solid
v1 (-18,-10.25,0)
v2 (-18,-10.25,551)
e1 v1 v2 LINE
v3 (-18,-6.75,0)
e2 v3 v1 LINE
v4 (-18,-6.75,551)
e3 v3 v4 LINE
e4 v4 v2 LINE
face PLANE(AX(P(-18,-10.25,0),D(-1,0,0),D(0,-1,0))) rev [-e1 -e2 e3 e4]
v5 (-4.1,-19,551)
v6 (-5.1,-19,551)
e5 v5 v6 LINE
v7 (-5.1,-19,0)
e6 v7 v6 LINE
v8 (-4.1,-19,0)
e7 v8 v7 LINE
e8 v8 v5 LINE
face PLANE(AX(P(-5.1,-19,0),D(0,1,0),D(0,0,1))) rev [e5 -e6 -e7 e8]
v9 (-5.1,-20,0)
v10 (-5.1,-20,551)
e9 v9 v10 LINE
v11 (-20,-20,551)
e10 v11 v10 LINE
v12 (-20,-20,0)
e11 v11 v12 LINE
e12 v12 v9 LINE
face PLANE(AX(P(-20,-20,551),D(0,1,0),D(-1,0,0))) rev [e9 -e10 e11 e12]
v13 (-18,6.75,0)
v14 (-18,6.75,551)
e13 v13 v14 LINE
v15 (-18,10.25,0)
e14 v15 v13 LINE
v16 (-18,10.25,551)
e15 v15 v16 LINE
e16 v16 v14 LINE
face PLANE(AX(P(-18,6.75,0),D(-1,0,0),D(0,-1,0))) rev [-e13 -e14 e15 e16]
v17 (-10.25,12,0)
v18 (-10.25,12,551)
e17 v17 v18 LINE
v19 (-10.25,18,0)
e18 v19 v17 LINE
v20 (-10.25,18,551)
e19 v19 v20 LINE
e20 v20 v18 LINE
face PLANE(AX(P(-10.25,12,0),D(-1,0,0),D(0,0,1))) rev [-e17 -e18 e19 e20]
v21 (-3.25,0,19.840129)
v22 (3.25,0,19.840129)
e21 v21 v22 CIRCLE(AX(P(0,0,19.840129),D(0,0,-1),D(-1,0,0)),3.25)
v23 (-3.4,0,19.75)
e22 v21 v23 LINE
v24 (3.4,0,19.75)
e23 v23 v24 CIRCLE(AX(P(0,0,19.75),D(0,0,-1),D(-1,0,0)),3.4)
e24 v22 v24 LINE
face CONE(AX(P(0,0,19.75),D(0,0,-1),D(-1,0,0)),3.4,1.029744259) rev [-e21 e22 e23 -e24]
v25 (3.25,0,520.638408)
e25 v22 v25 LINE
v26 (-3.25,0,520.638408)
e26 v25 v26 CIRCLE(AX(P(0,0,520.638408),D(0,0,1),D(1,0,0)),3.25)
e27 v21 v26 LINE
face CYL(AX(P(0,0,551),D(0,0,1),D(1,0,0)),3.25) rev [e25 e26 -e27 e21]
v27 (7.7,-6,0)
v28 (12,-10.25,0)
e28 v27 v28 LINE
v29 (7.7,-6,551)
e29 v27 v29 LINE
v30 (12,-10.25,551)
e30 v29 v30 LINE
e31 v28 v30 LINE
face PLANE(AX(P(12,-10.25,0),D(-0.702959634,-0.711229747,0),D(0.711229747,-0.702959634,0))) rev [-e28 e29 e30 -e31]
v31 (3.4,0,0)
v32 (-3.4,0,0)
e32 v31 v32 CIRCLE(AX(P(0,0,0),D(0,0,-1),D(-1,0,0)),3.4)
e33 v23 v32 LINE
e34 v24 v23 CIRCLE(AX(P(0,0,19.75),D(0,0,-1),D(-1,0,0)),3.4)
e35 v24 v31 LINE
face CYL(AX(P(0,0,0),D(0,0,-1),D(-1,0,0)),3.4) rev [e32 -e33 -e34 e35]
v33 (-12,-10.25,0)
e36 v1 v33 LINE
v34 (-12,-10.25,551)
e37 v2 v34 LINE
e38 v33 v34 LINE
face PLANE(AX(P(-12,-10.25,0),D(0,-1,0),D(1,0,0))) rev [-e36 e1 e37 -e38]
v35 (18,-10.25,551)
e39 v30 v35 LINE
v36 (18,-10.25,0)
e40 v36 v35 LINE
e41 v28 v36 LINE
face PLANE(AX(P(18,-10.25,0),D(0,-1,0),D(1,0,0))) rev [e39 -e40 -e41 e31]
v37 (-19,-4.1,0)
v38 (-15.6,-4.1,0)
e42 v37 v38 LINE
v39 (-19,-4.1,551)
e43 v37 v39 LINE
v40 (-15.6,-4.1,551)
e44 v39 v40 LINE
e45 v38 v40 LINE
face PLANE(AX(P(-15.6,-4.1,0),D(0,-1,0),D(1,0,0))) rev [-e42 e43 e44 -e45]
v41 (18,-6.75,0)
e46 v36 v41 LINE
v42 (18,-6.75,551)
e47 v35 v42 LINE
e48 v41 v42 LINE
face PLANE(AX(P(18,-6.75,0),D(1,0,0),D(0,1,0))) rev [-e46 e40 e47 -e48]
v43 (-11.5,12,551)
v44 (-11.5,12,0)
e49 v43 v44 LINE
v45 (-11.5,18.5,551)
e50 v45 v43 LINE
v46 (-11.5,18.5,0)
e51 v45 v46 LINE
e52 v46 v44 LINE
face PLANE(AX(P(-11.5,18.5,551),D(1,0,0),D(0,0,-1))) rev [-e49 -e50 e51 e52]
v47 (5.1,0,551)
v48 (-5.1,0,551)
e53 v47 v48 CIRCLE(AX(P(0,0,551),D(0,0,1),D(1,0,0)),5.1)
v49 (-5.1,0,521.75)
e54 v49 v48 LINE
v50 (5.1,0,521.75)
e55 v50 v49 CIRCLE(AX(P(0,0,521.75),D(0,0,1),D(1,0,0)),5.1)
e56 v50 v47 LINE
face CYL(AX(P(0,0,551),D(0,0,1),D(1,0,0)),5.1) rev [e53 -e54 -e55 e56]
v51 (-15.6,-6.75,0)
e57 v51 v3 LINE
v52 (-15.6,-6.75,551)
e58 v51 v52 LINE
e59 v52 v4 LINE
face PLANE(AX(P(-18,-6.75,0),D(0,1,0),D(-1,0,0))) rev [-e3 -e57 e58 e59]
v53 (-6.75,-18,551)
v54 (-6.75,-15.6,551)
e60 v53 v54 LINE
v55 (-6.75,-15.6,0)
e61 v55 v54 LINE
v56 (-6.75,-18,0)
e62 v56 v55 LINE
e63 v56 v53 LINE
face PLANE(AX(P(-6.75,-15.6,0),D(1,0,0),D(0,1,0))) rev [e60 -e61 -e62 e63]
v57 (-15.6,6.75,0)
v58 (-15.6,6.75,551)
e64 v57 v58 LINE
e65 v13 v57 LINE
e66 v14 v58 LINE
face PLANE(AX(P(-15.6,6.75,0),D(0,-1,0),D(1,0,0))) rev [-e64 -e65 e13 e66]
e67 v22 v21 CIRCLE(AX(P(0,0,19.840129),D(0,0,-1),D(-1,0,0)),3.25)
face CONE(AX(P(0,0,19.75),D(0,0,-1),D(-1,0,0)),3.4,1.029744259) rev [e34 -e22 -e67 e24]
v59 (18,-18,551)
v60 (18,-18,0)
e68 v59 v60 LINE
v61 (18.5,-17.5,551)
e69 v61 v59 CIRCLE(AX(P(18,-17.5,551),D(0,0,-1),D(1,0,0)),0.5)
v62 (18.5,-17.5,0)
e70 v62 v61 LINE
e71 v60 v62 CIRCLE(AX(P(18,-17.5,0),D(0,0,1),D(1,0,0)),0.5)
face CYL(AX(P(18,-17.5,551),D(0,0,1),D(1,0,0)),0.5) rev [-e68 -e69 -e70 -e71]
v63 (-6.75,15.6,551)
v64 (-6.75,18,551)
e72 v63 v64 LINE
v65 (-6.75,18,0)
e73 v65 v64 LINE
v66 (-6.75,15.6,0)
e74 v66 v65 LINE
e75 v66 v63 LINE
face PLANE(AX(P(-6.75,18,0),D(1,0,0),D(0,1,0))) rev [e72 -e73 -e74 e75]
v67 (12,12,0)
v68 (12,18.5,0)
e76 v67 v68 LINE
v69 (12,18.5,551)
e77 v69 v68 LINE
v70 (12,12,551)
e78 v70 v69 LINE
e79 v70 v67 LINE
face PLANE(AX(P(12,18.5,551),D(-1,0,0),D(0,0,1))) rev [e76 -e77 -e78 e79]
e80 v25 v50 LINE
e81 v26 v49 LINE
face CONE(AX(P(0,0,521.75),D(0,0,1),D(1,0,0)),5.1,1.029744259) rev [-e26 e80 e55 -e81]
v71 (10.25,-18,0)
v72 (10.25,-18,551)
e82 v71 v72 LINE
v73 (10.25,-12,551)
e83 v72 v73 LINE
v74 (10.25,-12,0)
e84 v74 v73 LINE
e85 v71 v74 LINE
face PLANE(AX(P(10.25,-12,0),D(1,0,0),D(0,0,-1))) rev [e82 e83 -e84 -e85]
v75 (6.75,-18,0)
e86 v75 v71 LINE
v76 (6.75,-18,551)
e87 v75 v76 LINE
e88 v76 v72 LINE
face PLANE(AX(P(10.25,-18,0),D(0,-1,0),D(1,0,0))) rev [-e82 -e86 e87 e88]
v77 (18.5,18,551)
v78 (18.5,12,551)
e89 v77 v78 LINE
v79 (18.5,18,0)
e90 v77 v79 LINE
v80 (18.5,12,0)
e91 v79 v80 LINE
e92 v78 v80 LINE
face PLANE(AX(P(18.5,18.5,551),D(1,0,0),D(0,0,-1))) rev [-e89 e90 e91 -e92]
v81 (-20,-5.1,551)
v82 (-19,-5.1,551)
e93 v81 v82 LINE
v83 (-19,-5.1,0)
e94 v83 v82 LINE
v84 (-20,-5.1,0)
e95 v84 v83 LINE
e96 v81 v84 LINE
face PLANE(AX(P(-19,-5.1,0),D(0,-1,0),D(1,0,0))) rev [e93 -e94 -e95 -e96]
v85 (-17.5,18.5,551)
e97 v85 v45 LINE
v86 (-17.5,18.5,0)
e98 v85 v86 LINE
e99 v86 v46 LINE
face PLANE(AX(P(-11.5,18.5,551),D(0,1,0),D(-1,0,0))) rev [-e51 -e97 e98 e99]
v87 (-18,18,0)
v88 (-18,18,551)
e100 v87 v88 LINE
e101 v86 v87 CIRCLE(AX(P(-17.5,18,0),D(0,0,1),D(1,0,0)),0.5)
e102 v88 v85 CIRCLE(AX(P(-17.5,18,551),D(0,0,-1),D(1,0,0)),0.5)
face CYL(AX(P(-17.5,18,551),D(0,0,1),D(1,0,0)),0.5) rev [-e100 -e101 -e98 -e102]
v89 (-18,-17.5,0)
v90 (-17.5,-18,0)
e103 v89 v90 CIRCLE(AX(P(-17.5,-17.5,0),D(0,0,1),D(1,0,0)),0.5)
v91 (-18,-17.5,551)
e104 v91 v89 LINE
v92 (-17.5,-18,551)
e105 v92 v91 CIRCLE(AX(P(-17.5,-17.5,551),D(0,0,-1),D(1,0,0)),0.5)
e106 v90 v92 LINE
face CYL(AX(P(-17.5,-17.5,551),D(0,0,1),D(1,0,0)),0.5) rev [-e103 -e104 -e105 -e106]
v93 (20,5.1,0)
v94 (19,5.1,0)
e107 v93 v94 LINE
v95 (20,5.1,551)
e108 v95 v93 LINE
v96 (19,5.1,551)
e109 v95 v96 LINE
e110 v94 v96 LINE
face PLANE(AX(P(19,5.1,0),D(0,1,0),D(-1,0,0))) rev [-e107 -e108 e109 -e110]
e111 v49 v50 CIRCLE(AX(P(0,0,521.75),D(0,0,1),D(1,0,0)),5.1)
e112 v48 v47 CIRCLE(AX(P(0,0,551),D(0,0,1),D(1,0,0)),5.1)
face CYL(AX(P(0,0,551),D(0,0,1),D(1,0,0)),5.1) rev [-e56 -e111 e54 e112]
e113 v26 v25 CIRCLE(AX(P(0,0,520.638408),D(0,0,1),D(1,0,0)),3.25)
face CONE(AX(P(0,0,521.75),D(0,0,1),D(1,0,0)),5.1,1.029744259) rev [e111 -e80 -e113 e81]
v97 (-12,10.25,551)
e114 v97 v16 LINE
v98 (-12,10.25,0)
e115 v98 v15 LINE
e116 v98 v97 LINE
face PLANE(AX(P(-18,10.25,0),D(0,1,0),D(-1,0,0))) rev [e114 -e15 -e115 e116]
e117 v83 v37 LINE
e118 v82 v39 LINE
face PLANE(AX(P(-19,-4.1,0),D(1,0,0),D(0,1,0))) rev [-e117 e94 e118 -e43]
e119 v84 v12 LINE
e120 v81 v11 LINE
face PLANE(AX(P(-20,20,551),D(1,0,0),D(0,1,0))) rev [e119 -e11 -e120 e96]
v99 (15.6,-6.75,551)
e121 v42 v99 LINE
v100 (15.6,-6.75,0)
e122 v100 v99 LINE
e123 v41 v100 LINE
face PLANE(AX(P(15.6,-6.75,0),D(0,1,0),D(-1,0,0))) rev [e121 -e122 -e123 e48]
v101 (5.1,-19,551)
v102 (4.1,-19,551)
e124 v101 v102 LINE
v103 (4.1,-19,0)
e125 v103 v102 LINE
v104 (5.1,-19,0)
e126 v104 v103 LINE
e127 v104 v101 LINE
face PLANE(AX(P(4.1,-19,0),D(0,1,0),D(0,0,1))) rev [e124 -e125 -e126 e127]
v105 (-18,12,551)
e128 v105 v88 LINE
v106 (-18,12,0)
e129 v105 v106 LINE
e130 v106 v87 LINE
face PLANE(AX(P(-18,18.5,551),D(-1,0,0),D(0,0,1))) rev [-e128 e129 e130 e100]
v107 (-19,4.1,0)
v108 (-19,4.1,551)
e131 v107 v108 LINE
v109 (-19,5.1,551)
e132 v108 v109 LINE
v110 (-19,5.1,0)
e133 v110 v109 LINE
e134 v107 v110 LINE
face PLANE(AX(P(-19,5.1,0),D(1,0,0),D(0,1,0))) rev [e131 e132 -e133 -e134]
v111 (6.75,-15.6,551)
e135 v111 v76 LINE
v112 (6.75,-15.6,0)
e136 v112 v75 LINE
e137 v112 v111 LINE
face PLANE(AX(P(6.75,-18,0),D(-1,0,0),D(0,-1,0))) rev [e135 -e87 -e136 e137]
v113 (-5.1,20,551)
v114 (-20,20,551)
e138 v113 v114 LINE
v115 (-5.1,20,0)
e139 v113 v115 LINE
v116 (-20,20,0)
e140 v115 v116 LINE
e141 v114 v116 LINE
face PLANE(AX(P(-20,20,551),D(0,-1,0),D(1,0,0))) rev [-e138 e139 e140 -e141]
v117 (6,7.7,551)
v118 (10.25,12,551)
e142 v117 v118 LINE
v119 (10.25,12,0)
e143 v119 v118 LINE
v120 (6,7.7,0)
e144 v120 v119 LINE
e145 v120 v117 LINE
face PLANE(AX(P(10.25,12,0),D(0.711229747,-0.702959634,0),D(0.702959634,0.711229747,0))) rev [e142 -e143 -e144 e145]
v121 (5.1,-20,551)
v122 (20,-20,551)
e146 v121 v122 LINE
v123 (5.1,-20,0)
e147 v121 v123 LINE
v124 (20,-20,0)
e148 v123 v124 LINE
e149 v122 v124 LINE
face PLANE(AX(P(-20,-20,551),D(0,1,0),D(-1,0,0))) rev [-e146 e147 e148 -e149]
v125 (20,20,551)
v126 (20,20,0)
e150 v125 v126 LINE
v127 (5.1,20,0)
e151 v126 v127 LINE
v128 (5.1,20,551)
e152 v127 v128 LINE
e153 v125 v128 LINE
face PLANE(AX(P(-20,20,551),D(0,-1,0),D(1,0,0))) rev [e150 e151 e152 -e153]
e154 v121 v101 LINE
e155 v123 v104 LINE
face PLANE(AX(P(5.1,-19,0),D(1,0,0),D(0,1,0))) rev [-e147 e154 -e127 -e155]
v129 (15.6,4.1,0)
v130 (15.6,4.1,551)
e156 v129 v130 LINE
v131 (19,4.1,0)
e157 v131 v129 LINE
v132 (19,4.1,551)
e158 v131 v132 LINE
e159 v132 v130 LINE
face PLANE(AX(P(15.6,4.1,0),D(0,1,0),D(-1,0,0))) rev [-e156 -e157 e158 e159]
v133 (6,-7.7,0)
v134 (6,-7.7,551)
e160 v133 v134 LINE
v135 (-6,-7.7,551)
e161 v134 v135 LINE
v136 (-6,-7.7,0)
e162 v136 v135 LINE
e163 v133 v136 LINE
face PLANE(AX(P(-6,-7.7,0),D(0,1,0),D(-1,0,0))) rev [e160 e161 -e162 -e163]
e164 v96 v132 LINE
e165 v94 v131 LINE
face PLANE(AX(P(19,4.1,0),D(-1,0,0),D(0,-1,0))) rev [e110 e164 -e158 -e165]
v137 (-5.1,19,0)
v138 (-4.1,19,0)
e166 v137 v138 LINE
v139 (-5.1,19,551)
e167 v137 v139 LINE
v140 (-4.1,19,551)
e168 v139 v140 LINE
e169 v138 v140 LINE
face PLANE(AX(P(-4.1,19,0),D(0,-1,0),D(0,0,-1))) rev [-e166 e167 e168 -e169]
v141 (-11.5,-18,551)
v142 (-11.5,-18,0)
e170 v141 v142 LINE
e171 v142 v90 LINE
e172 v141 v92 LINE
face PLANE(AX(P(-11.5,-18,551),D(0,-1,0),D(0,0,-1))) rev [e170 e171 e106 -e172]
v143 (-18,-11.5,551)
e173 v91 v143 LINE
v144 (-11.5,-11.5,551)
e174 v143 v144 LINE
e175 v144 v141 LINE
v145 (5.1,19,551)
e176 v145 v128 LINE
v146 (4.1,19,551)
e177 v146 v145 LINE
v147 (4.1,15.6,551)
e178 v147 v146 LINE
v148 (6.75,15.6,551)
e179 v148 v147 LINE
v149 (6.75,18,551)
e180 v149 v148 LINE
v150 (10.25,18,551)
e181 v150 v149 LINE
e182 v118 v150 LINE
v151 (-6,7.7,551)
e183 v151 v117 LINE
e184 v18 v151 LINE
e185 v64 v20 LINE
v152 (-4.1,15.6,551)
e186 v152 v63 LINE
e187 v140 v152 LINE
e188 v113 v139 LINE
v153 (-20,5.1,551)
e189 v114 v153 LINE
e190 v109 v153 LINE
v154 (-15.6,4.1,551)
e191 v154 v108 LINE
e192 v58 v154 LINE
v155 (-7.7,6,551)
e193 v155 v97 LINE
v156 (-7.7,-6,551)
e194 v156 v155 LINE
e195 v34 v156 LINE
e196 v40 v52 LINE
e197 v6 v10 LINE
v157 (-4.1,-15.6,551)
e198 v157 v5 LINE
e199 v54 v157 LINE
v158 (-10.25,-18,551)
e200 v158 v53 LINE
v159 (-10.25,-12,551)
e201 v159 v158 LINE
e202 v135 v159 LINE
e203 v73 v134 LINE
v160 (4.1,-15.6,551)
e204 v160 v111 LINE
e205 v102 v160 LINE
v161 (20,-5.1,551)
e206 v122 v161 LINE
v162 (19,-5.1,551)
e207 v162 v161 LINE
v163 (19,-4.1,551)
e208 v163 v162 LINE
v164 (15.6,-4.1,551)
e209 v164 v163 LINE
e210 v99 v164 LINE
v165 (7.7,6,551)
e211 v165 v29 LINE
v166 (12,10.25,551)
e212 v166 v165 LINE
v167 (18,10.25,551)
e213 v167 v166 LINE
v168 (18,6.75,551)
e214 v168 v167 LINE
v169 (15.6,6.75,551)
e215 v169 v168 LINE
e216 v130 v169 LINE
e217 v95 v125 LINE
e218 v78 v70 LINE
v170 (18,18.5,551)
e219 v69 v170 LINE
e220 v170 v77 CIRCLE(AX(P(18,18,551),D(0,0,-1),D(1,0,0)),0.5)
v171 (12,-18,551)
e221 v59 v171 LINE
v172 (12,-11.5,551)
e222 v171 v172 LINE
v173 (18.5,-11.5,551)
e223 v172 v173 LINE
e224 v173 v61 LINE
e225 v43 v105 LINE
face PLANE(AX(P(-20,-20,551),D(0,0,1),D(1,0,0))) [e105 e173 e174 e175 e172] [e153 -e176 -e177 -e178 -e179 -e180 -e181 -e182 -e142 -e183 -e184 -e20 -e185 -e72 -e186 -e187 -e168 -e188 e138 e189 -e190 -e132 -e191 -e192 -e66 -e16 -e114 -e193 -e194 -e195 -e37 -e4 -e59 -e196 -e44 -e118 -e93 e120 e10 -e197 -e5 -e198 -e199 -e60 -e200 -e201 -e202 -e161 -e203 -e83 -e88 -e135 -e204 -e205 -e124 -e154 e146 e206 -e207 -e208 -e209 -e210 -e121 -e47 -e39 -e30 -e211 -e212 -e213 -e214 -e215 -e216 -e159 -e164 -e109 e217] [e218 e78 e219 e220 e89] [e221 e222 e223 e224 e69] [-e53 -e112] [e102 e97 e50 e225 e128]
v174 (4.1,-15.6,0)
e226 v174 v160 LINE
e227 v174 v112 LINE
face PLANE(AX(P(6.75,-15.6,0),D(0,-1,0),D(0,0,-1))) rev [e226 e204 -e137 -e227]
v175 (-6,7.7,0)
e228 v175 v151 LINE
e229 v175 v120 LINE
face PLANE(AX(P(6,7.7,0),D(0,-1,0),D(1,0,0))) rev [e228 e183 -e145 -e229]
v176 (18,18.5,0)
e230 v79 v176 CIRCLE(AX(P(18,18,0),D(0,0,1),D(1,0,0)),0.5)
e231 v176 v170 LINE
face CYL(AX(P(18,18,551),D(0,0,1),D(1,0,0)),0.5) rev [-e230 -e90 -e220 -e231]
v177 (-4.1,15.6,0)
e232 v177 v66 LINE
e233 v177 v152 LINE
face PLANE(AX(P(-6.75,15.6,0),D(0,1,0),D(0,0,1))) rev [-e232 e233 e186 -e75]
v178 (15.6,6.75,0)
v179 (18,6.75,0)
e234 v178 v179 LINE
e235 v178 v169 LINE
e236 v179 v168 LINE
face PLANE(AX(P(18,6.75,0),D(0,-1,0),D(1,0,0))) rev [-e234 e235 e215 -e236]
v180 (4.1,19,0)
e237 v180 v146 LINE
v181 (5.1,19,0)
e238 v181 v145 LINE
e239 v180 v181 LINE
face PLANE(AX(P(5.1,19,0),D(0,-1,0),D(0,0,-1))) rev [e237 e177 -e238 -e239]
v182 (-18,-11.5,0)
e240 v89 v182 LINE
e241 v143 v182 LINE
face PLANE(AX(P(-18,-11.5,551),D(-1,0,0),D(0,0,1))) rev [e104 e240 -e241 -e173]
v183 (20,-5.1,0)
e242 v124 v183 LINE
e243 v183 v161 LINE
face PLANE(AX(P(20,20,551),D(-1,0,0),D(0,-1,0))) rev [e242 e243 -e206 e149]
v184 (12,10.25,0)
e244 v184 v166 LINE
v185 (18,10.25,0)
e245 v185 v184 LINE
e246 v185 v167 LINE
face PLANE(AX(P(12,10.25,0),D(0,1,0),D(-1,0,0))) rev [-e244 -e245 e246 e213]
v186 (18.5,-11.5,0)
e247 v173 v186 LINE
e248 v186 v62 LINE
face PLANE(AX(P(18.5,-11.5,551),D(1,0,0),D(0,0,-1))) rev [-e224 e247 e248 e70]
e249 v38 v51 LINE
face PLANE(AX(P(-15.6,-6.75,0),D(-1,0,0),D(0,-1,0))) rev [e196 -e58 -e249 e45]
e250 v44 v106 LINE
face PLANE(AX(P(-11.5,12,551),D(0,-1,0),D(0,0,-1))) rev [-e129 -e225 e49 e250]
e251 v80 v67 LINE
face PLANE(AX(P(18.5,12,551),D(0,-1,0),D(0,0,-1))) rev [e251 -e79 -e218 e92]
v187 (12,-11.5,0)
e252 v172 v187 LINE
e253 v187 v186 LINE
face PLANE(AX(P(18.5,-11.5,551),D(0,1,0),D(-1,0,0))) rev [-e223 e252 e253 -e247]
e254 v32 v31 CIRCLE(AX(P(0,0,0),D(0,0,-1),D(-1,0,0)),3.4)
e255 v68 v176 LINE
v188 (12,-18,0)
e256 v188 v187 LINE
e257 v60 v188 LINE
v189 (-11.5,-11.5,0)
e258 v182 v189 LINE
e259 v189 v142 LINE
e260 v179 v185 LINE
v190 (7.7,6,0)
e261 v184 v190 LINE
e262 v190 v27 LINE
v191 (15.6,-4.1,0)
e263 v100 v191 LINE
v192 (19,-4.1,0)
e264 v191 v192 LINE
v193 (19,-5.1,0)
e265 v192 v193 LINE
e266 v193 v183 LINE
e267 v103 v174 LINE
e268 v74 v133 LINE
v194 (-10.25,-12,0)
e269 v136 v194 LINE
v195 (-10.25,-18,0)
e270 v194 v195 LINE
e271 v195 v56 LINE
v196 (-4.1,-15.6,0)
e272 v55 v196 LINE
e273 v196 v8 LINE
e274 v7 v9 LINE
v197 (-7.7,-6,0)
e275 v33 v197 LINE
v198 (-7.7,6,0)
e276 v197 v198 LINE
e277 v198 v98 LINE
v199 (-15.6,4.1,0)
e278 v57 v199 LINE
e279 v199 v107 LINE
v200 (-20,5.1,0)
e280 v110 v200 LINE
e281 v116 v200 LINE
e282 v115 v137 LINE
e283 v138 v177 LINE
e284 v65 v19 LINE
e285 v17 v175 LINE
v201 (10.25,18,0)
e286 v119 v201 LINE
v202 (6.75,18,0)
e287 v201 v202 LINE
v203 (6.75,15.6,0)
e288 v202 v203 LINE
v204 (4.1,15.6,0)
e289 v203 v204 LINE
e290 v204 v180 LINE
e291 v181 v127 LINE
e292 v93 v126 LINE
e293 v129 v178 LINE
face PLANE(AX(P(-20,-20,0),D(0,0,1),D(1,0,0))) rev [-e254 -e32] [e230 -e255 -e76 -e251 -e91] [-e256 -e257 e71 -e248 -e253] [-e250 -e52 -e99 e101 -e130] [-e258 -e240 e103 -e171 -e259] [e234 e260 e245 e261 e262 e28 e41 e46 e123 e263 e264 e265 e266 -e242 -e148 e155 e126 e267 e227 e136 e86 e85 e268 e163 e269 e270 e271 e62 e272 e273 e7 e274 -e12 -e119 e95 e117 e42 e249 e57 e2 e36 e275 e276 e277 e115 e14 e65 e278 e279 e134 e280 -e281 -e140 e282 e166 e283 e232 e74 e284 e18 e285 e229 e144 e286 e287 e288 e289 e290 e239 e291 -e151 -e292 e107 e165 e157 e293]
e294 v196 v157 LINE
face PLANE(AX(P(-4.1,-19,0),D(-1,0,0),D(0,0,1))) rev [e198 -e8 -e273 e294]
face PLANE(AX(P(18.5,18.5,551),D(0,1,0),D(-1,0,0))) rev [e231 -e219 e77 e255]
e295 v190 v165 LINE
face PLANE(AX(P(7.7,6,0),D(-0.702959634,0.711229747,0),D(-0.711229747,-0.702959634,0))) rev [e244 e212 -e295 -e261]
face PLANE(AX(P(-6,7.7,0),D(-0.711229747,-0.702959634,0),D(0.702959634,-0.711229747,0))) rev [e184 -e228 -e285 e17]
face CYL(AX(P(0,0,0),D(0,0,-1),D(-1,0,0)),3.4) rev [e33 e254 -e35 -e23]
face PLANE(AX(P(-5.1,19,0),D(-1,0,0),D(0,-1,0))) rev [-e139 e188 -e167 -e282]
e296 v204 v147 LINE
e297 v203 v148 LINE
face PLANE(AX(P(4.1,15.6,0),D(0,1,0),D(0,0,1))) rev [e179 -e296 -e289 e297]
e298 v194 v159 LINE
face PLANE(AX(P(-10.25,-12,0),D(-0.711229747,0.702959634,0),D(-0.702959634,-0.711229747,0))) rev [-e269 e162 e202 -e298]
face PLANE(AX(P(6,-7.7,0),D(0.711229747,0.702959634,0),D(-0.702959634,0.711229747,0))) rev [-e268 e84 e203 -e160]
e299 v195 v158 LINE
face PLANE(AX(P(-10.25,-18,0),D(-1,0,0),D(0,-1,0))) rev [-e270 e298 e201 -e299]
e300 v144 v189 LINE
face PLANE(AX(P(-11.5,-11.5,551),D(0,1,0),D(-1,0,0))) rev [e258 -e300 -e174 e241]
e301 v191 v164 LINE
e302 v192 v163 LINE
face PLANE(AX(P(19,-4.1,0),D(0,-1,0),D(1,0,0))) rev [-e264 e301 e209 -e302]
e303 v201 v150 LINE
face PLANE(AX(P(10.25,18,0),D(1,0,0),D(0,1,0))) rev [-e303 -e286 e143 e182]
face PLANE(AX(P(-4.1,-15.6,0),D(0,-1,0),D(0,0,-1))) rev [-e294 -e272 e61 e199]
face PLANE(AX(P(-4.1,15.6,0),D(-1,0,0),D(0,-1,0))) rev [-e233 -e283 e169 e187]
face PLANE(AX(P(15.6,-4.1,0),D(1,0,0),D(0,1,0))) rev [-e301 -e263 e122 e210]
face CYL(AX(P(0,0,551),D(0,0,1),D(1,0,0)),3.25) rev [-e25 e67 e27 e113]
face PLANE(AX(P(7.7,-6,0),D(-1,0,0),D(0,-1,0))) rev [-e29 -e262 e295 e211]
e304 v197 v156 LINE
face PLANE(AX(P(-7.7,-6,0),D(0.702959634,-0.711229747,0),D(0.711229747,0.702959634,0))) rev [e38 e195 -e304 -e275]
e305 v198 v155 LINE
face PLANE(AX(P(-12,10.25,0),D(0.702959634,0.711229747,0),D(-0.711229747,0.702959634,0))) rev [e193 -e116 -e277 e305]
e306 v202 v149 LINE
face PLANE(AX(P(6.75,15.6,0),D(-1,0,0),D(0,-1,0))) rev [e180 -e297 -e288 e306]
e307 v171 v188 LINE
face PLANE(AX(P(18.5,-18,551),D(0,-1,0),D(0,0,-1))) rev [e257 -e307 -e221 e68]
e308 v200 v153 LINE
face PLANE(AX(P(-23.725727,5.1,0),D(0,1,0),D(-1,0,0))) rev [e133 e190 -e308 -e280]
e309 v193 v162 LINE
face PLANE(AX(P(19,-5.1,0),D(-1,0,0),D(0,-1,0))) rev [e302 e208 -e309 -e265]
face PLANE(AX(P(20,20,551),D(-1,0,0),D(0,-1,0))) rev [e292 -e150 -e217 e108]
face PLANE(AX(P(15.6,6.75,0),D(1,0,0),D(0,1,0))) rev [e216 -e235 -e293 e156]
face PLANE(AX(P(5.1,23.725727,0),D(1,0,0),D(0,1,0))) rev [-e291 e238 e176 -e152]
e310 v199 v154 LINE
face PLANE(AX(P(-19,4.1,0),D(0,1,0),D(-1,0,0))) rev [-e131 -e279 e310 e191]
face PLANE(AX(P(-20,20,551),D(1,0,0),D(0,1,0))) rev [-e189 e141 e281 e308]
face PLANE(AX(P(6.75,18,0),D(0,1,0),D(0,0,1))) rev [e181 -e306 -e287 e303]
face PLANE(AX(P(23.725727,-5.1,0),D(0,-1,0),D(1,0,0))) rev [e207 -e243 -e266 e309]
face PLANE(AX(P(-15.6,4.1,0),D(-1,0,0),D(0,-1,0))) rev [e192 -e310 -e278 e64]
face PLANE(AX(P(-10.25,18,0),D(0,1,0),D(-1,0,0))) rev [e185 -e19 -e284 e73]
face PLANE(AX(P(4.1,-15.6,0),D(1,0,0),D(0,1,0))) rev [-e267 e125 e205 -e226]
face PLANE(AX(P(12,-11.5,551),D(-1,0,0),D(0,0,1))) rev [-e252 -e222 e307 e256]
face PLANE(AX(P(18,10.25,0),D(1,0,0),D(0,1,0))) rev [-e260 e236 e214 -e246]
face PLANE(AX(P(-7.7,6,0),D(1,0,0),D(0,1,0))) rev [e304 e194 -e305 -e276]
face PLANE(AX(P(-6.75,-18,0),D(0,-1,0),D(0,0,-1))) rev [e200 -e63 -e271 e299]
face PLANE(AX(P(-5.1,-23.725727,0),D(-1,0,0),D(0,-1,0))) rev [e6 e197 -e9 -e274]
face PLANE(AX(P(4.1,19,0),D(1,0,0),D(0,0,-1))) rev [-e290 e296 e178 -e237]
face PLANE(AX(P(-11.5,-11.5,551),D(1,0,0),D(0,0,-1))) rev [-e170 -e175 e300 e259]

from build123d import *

# Parameters (mm, degrees)
SKETCH_1_W                  = 40
SKETCH_1_H                  = 40
EXTRUDE_1_DEPTH             = 551
HOLE_WIZARD_6_5_6_5_1_D     = 6.5
CUT_EXTRUDE_1_DEPTH         = 552.725475214
PATTERN_CIRCULAR_1_COUNT    = 4
SKETCH_5_W                  = 6.5
SKETCH_5_H                  = 6.5
CUT_EXTRUDE_2_DEPTH         = 552.725475214
PATTERN_LINEAR_1_COUNT      = 2
PATTERN_LINEAR_1_PITCH      = 30
PATTERN_LINEAR_1_COUNT_DIR2 = 2
PATTERN_LINEAR_1_PITCH_DIR2 = 30
FILLET_2_R                  = 0.5
HOLE_WIZARD_M12_1_D         = 10.2
HOLE_WIZARD_M12_1_DEPTH     = 29.25
HOLE_WIZARD_M12_1_TIP       = 3.064389157
HOLE_WIZARD_M8_2_D          = 6.8
HOLE_WIZARD_M8_2_DEPTH      = 19.75
HOLE_WIZARD_M8_2_TIP        = 2.042926105


with BuildPart() as part:
    # 草图1 → 凸台-拉伸1 (new body)
    with BuildSketch(Plane.XY):
        Rectangle(SKETCH_1_W, SKETCH_1_H)
    extrude(amount=EXTRUDE_1_DEPTH)

    # Ø6.5 (6.5) 直径孔1 (through all)
    with Locations(Plane.XY.offset(551)):
        with Locations((0, 0)):
            Hole(HOLE_WIZARD_6_5_6_5_1_D / 2)

    # 草图4 → 切除-拉伸1 (cut, through all)
    with BuildSketch(Plane.XY.offset(551)):
        Polygon((6, -7.7), (10.25, -12), (10.25, -18), (6.75, -18), (6.75, -15.6), (4.1, -15.6), (4.1, -19), (5.1, -19), (5.1, -23.725727051), (-5.1, -23.725727051), (-5.1, -19), (-4.1, -19), (-4.1, -15.6), (-6.75, -15.6), (-6.75, -18), (-10.25, -18), (-10.25, -12), (-6, -7.7), align=None)
    cut_extrude_1 = extrude(amount=-CUT_EXTRUDE_1_DEPTH, mode=Mode.SUBTRACT)

    # 阵列(圆周)1: 切除-拉伸1 ×4 about axis
    pattern_circular_1_axis = Axis((0, 0, 0), (0, 0, 1))
    for i in range(1, PATTERN_CIRCULAR_1_COUNT):
        add(cut_extrude_1.rotate(pattern_circular_1_axis, i * 360 / PATTERN_CIRCULAR_1_COUNT), mode=Mode.SUBTRACT)

    # 草图5 → 切除-拉伸2 (cut, through all)
    with BuildSketch(Plane(origin=(0, 0, 0), x_dir=(-1, 0, 0), z_dir=(0, 0, -1))):
        with Locations((14.75, -14.75)):
            Rectangle(SKETCH_5_W, SKETCH_5_H)
    cut_extrude_2 = extrude(amount=-CUT_EXTRUDE_2_DEPTH, mode=Mode.SUBTRACT)

    # 阵列(线性)1: Cut-Extrude 2 2 × 2
    with Locations(*[(i * PATTERN_LINEAR_1_PITCH, j * PATTERN_LINEAR_1_PITCH_DIR2, 0) for i in range(PATTERN_LINEAR_1_COUNT) for j in range(PATTERN_LINEAR_1_COUNT_DIR2) if (i, j) != (0, 0)]):
        add(cut_extrude_2, mode=Mode.SUBTRACT)

    # 圆角2
    fillet_2_edges = [part.edges().sort_by_distance(p)[0] for p in [
        (-18, -18, 275.5),
        (18.5, -18, 275.5),
        (-18, 18.5, 275.5),
        (18.5, 18.5, 275.5),
    ]]
    fillet(fillet_2_edges, radius=FILLET_2_R)

    # M12 螺纹孔1
    with Locations(Plane.XY.offset(551)):
        with Locations((0, 0)):
            Hole(HOLE_WIZARD_M12_1_D / 2, depth=HOLE_WIZARD_M12_1_DEPTH)
            with Locations((0, 0, -(HOLE_WIZARD_M12_1_DEPTH + HOLE_WIZARD_M12_1_TIP / 2))):  # 118° drill point
                Cone(0, HOLE_WIZARD_M12_1_D / 2, HOLE_WIZARD_M12_1_TIP, mode=Mode.SUBTRACT)

    # M8 螺纹孔2
    with Locations(Plane(origin=(0, 0, 0), x_dir=(-1, 0, 0), z_dir=(0, 0, -1))):
        with Locations((0, 0)):
            Hole(HOLE_WIZARD_M8_2_D / 2, depth=HOLE_WIZARD_M8_2_DEPTH)
            with Locations((0, 0, -(HOLE_WIZARD_M8_2_DEPTH + HOLE_WIZARD_M8_2_TIP / 2))):  # 118° drill point
                Cone(0, HOLE_WIZARD_M8_2_D / 2, HOLE_WIZARD_M8_2_TIP, mode=Mode.SUBTRACT)


solid = part.part
